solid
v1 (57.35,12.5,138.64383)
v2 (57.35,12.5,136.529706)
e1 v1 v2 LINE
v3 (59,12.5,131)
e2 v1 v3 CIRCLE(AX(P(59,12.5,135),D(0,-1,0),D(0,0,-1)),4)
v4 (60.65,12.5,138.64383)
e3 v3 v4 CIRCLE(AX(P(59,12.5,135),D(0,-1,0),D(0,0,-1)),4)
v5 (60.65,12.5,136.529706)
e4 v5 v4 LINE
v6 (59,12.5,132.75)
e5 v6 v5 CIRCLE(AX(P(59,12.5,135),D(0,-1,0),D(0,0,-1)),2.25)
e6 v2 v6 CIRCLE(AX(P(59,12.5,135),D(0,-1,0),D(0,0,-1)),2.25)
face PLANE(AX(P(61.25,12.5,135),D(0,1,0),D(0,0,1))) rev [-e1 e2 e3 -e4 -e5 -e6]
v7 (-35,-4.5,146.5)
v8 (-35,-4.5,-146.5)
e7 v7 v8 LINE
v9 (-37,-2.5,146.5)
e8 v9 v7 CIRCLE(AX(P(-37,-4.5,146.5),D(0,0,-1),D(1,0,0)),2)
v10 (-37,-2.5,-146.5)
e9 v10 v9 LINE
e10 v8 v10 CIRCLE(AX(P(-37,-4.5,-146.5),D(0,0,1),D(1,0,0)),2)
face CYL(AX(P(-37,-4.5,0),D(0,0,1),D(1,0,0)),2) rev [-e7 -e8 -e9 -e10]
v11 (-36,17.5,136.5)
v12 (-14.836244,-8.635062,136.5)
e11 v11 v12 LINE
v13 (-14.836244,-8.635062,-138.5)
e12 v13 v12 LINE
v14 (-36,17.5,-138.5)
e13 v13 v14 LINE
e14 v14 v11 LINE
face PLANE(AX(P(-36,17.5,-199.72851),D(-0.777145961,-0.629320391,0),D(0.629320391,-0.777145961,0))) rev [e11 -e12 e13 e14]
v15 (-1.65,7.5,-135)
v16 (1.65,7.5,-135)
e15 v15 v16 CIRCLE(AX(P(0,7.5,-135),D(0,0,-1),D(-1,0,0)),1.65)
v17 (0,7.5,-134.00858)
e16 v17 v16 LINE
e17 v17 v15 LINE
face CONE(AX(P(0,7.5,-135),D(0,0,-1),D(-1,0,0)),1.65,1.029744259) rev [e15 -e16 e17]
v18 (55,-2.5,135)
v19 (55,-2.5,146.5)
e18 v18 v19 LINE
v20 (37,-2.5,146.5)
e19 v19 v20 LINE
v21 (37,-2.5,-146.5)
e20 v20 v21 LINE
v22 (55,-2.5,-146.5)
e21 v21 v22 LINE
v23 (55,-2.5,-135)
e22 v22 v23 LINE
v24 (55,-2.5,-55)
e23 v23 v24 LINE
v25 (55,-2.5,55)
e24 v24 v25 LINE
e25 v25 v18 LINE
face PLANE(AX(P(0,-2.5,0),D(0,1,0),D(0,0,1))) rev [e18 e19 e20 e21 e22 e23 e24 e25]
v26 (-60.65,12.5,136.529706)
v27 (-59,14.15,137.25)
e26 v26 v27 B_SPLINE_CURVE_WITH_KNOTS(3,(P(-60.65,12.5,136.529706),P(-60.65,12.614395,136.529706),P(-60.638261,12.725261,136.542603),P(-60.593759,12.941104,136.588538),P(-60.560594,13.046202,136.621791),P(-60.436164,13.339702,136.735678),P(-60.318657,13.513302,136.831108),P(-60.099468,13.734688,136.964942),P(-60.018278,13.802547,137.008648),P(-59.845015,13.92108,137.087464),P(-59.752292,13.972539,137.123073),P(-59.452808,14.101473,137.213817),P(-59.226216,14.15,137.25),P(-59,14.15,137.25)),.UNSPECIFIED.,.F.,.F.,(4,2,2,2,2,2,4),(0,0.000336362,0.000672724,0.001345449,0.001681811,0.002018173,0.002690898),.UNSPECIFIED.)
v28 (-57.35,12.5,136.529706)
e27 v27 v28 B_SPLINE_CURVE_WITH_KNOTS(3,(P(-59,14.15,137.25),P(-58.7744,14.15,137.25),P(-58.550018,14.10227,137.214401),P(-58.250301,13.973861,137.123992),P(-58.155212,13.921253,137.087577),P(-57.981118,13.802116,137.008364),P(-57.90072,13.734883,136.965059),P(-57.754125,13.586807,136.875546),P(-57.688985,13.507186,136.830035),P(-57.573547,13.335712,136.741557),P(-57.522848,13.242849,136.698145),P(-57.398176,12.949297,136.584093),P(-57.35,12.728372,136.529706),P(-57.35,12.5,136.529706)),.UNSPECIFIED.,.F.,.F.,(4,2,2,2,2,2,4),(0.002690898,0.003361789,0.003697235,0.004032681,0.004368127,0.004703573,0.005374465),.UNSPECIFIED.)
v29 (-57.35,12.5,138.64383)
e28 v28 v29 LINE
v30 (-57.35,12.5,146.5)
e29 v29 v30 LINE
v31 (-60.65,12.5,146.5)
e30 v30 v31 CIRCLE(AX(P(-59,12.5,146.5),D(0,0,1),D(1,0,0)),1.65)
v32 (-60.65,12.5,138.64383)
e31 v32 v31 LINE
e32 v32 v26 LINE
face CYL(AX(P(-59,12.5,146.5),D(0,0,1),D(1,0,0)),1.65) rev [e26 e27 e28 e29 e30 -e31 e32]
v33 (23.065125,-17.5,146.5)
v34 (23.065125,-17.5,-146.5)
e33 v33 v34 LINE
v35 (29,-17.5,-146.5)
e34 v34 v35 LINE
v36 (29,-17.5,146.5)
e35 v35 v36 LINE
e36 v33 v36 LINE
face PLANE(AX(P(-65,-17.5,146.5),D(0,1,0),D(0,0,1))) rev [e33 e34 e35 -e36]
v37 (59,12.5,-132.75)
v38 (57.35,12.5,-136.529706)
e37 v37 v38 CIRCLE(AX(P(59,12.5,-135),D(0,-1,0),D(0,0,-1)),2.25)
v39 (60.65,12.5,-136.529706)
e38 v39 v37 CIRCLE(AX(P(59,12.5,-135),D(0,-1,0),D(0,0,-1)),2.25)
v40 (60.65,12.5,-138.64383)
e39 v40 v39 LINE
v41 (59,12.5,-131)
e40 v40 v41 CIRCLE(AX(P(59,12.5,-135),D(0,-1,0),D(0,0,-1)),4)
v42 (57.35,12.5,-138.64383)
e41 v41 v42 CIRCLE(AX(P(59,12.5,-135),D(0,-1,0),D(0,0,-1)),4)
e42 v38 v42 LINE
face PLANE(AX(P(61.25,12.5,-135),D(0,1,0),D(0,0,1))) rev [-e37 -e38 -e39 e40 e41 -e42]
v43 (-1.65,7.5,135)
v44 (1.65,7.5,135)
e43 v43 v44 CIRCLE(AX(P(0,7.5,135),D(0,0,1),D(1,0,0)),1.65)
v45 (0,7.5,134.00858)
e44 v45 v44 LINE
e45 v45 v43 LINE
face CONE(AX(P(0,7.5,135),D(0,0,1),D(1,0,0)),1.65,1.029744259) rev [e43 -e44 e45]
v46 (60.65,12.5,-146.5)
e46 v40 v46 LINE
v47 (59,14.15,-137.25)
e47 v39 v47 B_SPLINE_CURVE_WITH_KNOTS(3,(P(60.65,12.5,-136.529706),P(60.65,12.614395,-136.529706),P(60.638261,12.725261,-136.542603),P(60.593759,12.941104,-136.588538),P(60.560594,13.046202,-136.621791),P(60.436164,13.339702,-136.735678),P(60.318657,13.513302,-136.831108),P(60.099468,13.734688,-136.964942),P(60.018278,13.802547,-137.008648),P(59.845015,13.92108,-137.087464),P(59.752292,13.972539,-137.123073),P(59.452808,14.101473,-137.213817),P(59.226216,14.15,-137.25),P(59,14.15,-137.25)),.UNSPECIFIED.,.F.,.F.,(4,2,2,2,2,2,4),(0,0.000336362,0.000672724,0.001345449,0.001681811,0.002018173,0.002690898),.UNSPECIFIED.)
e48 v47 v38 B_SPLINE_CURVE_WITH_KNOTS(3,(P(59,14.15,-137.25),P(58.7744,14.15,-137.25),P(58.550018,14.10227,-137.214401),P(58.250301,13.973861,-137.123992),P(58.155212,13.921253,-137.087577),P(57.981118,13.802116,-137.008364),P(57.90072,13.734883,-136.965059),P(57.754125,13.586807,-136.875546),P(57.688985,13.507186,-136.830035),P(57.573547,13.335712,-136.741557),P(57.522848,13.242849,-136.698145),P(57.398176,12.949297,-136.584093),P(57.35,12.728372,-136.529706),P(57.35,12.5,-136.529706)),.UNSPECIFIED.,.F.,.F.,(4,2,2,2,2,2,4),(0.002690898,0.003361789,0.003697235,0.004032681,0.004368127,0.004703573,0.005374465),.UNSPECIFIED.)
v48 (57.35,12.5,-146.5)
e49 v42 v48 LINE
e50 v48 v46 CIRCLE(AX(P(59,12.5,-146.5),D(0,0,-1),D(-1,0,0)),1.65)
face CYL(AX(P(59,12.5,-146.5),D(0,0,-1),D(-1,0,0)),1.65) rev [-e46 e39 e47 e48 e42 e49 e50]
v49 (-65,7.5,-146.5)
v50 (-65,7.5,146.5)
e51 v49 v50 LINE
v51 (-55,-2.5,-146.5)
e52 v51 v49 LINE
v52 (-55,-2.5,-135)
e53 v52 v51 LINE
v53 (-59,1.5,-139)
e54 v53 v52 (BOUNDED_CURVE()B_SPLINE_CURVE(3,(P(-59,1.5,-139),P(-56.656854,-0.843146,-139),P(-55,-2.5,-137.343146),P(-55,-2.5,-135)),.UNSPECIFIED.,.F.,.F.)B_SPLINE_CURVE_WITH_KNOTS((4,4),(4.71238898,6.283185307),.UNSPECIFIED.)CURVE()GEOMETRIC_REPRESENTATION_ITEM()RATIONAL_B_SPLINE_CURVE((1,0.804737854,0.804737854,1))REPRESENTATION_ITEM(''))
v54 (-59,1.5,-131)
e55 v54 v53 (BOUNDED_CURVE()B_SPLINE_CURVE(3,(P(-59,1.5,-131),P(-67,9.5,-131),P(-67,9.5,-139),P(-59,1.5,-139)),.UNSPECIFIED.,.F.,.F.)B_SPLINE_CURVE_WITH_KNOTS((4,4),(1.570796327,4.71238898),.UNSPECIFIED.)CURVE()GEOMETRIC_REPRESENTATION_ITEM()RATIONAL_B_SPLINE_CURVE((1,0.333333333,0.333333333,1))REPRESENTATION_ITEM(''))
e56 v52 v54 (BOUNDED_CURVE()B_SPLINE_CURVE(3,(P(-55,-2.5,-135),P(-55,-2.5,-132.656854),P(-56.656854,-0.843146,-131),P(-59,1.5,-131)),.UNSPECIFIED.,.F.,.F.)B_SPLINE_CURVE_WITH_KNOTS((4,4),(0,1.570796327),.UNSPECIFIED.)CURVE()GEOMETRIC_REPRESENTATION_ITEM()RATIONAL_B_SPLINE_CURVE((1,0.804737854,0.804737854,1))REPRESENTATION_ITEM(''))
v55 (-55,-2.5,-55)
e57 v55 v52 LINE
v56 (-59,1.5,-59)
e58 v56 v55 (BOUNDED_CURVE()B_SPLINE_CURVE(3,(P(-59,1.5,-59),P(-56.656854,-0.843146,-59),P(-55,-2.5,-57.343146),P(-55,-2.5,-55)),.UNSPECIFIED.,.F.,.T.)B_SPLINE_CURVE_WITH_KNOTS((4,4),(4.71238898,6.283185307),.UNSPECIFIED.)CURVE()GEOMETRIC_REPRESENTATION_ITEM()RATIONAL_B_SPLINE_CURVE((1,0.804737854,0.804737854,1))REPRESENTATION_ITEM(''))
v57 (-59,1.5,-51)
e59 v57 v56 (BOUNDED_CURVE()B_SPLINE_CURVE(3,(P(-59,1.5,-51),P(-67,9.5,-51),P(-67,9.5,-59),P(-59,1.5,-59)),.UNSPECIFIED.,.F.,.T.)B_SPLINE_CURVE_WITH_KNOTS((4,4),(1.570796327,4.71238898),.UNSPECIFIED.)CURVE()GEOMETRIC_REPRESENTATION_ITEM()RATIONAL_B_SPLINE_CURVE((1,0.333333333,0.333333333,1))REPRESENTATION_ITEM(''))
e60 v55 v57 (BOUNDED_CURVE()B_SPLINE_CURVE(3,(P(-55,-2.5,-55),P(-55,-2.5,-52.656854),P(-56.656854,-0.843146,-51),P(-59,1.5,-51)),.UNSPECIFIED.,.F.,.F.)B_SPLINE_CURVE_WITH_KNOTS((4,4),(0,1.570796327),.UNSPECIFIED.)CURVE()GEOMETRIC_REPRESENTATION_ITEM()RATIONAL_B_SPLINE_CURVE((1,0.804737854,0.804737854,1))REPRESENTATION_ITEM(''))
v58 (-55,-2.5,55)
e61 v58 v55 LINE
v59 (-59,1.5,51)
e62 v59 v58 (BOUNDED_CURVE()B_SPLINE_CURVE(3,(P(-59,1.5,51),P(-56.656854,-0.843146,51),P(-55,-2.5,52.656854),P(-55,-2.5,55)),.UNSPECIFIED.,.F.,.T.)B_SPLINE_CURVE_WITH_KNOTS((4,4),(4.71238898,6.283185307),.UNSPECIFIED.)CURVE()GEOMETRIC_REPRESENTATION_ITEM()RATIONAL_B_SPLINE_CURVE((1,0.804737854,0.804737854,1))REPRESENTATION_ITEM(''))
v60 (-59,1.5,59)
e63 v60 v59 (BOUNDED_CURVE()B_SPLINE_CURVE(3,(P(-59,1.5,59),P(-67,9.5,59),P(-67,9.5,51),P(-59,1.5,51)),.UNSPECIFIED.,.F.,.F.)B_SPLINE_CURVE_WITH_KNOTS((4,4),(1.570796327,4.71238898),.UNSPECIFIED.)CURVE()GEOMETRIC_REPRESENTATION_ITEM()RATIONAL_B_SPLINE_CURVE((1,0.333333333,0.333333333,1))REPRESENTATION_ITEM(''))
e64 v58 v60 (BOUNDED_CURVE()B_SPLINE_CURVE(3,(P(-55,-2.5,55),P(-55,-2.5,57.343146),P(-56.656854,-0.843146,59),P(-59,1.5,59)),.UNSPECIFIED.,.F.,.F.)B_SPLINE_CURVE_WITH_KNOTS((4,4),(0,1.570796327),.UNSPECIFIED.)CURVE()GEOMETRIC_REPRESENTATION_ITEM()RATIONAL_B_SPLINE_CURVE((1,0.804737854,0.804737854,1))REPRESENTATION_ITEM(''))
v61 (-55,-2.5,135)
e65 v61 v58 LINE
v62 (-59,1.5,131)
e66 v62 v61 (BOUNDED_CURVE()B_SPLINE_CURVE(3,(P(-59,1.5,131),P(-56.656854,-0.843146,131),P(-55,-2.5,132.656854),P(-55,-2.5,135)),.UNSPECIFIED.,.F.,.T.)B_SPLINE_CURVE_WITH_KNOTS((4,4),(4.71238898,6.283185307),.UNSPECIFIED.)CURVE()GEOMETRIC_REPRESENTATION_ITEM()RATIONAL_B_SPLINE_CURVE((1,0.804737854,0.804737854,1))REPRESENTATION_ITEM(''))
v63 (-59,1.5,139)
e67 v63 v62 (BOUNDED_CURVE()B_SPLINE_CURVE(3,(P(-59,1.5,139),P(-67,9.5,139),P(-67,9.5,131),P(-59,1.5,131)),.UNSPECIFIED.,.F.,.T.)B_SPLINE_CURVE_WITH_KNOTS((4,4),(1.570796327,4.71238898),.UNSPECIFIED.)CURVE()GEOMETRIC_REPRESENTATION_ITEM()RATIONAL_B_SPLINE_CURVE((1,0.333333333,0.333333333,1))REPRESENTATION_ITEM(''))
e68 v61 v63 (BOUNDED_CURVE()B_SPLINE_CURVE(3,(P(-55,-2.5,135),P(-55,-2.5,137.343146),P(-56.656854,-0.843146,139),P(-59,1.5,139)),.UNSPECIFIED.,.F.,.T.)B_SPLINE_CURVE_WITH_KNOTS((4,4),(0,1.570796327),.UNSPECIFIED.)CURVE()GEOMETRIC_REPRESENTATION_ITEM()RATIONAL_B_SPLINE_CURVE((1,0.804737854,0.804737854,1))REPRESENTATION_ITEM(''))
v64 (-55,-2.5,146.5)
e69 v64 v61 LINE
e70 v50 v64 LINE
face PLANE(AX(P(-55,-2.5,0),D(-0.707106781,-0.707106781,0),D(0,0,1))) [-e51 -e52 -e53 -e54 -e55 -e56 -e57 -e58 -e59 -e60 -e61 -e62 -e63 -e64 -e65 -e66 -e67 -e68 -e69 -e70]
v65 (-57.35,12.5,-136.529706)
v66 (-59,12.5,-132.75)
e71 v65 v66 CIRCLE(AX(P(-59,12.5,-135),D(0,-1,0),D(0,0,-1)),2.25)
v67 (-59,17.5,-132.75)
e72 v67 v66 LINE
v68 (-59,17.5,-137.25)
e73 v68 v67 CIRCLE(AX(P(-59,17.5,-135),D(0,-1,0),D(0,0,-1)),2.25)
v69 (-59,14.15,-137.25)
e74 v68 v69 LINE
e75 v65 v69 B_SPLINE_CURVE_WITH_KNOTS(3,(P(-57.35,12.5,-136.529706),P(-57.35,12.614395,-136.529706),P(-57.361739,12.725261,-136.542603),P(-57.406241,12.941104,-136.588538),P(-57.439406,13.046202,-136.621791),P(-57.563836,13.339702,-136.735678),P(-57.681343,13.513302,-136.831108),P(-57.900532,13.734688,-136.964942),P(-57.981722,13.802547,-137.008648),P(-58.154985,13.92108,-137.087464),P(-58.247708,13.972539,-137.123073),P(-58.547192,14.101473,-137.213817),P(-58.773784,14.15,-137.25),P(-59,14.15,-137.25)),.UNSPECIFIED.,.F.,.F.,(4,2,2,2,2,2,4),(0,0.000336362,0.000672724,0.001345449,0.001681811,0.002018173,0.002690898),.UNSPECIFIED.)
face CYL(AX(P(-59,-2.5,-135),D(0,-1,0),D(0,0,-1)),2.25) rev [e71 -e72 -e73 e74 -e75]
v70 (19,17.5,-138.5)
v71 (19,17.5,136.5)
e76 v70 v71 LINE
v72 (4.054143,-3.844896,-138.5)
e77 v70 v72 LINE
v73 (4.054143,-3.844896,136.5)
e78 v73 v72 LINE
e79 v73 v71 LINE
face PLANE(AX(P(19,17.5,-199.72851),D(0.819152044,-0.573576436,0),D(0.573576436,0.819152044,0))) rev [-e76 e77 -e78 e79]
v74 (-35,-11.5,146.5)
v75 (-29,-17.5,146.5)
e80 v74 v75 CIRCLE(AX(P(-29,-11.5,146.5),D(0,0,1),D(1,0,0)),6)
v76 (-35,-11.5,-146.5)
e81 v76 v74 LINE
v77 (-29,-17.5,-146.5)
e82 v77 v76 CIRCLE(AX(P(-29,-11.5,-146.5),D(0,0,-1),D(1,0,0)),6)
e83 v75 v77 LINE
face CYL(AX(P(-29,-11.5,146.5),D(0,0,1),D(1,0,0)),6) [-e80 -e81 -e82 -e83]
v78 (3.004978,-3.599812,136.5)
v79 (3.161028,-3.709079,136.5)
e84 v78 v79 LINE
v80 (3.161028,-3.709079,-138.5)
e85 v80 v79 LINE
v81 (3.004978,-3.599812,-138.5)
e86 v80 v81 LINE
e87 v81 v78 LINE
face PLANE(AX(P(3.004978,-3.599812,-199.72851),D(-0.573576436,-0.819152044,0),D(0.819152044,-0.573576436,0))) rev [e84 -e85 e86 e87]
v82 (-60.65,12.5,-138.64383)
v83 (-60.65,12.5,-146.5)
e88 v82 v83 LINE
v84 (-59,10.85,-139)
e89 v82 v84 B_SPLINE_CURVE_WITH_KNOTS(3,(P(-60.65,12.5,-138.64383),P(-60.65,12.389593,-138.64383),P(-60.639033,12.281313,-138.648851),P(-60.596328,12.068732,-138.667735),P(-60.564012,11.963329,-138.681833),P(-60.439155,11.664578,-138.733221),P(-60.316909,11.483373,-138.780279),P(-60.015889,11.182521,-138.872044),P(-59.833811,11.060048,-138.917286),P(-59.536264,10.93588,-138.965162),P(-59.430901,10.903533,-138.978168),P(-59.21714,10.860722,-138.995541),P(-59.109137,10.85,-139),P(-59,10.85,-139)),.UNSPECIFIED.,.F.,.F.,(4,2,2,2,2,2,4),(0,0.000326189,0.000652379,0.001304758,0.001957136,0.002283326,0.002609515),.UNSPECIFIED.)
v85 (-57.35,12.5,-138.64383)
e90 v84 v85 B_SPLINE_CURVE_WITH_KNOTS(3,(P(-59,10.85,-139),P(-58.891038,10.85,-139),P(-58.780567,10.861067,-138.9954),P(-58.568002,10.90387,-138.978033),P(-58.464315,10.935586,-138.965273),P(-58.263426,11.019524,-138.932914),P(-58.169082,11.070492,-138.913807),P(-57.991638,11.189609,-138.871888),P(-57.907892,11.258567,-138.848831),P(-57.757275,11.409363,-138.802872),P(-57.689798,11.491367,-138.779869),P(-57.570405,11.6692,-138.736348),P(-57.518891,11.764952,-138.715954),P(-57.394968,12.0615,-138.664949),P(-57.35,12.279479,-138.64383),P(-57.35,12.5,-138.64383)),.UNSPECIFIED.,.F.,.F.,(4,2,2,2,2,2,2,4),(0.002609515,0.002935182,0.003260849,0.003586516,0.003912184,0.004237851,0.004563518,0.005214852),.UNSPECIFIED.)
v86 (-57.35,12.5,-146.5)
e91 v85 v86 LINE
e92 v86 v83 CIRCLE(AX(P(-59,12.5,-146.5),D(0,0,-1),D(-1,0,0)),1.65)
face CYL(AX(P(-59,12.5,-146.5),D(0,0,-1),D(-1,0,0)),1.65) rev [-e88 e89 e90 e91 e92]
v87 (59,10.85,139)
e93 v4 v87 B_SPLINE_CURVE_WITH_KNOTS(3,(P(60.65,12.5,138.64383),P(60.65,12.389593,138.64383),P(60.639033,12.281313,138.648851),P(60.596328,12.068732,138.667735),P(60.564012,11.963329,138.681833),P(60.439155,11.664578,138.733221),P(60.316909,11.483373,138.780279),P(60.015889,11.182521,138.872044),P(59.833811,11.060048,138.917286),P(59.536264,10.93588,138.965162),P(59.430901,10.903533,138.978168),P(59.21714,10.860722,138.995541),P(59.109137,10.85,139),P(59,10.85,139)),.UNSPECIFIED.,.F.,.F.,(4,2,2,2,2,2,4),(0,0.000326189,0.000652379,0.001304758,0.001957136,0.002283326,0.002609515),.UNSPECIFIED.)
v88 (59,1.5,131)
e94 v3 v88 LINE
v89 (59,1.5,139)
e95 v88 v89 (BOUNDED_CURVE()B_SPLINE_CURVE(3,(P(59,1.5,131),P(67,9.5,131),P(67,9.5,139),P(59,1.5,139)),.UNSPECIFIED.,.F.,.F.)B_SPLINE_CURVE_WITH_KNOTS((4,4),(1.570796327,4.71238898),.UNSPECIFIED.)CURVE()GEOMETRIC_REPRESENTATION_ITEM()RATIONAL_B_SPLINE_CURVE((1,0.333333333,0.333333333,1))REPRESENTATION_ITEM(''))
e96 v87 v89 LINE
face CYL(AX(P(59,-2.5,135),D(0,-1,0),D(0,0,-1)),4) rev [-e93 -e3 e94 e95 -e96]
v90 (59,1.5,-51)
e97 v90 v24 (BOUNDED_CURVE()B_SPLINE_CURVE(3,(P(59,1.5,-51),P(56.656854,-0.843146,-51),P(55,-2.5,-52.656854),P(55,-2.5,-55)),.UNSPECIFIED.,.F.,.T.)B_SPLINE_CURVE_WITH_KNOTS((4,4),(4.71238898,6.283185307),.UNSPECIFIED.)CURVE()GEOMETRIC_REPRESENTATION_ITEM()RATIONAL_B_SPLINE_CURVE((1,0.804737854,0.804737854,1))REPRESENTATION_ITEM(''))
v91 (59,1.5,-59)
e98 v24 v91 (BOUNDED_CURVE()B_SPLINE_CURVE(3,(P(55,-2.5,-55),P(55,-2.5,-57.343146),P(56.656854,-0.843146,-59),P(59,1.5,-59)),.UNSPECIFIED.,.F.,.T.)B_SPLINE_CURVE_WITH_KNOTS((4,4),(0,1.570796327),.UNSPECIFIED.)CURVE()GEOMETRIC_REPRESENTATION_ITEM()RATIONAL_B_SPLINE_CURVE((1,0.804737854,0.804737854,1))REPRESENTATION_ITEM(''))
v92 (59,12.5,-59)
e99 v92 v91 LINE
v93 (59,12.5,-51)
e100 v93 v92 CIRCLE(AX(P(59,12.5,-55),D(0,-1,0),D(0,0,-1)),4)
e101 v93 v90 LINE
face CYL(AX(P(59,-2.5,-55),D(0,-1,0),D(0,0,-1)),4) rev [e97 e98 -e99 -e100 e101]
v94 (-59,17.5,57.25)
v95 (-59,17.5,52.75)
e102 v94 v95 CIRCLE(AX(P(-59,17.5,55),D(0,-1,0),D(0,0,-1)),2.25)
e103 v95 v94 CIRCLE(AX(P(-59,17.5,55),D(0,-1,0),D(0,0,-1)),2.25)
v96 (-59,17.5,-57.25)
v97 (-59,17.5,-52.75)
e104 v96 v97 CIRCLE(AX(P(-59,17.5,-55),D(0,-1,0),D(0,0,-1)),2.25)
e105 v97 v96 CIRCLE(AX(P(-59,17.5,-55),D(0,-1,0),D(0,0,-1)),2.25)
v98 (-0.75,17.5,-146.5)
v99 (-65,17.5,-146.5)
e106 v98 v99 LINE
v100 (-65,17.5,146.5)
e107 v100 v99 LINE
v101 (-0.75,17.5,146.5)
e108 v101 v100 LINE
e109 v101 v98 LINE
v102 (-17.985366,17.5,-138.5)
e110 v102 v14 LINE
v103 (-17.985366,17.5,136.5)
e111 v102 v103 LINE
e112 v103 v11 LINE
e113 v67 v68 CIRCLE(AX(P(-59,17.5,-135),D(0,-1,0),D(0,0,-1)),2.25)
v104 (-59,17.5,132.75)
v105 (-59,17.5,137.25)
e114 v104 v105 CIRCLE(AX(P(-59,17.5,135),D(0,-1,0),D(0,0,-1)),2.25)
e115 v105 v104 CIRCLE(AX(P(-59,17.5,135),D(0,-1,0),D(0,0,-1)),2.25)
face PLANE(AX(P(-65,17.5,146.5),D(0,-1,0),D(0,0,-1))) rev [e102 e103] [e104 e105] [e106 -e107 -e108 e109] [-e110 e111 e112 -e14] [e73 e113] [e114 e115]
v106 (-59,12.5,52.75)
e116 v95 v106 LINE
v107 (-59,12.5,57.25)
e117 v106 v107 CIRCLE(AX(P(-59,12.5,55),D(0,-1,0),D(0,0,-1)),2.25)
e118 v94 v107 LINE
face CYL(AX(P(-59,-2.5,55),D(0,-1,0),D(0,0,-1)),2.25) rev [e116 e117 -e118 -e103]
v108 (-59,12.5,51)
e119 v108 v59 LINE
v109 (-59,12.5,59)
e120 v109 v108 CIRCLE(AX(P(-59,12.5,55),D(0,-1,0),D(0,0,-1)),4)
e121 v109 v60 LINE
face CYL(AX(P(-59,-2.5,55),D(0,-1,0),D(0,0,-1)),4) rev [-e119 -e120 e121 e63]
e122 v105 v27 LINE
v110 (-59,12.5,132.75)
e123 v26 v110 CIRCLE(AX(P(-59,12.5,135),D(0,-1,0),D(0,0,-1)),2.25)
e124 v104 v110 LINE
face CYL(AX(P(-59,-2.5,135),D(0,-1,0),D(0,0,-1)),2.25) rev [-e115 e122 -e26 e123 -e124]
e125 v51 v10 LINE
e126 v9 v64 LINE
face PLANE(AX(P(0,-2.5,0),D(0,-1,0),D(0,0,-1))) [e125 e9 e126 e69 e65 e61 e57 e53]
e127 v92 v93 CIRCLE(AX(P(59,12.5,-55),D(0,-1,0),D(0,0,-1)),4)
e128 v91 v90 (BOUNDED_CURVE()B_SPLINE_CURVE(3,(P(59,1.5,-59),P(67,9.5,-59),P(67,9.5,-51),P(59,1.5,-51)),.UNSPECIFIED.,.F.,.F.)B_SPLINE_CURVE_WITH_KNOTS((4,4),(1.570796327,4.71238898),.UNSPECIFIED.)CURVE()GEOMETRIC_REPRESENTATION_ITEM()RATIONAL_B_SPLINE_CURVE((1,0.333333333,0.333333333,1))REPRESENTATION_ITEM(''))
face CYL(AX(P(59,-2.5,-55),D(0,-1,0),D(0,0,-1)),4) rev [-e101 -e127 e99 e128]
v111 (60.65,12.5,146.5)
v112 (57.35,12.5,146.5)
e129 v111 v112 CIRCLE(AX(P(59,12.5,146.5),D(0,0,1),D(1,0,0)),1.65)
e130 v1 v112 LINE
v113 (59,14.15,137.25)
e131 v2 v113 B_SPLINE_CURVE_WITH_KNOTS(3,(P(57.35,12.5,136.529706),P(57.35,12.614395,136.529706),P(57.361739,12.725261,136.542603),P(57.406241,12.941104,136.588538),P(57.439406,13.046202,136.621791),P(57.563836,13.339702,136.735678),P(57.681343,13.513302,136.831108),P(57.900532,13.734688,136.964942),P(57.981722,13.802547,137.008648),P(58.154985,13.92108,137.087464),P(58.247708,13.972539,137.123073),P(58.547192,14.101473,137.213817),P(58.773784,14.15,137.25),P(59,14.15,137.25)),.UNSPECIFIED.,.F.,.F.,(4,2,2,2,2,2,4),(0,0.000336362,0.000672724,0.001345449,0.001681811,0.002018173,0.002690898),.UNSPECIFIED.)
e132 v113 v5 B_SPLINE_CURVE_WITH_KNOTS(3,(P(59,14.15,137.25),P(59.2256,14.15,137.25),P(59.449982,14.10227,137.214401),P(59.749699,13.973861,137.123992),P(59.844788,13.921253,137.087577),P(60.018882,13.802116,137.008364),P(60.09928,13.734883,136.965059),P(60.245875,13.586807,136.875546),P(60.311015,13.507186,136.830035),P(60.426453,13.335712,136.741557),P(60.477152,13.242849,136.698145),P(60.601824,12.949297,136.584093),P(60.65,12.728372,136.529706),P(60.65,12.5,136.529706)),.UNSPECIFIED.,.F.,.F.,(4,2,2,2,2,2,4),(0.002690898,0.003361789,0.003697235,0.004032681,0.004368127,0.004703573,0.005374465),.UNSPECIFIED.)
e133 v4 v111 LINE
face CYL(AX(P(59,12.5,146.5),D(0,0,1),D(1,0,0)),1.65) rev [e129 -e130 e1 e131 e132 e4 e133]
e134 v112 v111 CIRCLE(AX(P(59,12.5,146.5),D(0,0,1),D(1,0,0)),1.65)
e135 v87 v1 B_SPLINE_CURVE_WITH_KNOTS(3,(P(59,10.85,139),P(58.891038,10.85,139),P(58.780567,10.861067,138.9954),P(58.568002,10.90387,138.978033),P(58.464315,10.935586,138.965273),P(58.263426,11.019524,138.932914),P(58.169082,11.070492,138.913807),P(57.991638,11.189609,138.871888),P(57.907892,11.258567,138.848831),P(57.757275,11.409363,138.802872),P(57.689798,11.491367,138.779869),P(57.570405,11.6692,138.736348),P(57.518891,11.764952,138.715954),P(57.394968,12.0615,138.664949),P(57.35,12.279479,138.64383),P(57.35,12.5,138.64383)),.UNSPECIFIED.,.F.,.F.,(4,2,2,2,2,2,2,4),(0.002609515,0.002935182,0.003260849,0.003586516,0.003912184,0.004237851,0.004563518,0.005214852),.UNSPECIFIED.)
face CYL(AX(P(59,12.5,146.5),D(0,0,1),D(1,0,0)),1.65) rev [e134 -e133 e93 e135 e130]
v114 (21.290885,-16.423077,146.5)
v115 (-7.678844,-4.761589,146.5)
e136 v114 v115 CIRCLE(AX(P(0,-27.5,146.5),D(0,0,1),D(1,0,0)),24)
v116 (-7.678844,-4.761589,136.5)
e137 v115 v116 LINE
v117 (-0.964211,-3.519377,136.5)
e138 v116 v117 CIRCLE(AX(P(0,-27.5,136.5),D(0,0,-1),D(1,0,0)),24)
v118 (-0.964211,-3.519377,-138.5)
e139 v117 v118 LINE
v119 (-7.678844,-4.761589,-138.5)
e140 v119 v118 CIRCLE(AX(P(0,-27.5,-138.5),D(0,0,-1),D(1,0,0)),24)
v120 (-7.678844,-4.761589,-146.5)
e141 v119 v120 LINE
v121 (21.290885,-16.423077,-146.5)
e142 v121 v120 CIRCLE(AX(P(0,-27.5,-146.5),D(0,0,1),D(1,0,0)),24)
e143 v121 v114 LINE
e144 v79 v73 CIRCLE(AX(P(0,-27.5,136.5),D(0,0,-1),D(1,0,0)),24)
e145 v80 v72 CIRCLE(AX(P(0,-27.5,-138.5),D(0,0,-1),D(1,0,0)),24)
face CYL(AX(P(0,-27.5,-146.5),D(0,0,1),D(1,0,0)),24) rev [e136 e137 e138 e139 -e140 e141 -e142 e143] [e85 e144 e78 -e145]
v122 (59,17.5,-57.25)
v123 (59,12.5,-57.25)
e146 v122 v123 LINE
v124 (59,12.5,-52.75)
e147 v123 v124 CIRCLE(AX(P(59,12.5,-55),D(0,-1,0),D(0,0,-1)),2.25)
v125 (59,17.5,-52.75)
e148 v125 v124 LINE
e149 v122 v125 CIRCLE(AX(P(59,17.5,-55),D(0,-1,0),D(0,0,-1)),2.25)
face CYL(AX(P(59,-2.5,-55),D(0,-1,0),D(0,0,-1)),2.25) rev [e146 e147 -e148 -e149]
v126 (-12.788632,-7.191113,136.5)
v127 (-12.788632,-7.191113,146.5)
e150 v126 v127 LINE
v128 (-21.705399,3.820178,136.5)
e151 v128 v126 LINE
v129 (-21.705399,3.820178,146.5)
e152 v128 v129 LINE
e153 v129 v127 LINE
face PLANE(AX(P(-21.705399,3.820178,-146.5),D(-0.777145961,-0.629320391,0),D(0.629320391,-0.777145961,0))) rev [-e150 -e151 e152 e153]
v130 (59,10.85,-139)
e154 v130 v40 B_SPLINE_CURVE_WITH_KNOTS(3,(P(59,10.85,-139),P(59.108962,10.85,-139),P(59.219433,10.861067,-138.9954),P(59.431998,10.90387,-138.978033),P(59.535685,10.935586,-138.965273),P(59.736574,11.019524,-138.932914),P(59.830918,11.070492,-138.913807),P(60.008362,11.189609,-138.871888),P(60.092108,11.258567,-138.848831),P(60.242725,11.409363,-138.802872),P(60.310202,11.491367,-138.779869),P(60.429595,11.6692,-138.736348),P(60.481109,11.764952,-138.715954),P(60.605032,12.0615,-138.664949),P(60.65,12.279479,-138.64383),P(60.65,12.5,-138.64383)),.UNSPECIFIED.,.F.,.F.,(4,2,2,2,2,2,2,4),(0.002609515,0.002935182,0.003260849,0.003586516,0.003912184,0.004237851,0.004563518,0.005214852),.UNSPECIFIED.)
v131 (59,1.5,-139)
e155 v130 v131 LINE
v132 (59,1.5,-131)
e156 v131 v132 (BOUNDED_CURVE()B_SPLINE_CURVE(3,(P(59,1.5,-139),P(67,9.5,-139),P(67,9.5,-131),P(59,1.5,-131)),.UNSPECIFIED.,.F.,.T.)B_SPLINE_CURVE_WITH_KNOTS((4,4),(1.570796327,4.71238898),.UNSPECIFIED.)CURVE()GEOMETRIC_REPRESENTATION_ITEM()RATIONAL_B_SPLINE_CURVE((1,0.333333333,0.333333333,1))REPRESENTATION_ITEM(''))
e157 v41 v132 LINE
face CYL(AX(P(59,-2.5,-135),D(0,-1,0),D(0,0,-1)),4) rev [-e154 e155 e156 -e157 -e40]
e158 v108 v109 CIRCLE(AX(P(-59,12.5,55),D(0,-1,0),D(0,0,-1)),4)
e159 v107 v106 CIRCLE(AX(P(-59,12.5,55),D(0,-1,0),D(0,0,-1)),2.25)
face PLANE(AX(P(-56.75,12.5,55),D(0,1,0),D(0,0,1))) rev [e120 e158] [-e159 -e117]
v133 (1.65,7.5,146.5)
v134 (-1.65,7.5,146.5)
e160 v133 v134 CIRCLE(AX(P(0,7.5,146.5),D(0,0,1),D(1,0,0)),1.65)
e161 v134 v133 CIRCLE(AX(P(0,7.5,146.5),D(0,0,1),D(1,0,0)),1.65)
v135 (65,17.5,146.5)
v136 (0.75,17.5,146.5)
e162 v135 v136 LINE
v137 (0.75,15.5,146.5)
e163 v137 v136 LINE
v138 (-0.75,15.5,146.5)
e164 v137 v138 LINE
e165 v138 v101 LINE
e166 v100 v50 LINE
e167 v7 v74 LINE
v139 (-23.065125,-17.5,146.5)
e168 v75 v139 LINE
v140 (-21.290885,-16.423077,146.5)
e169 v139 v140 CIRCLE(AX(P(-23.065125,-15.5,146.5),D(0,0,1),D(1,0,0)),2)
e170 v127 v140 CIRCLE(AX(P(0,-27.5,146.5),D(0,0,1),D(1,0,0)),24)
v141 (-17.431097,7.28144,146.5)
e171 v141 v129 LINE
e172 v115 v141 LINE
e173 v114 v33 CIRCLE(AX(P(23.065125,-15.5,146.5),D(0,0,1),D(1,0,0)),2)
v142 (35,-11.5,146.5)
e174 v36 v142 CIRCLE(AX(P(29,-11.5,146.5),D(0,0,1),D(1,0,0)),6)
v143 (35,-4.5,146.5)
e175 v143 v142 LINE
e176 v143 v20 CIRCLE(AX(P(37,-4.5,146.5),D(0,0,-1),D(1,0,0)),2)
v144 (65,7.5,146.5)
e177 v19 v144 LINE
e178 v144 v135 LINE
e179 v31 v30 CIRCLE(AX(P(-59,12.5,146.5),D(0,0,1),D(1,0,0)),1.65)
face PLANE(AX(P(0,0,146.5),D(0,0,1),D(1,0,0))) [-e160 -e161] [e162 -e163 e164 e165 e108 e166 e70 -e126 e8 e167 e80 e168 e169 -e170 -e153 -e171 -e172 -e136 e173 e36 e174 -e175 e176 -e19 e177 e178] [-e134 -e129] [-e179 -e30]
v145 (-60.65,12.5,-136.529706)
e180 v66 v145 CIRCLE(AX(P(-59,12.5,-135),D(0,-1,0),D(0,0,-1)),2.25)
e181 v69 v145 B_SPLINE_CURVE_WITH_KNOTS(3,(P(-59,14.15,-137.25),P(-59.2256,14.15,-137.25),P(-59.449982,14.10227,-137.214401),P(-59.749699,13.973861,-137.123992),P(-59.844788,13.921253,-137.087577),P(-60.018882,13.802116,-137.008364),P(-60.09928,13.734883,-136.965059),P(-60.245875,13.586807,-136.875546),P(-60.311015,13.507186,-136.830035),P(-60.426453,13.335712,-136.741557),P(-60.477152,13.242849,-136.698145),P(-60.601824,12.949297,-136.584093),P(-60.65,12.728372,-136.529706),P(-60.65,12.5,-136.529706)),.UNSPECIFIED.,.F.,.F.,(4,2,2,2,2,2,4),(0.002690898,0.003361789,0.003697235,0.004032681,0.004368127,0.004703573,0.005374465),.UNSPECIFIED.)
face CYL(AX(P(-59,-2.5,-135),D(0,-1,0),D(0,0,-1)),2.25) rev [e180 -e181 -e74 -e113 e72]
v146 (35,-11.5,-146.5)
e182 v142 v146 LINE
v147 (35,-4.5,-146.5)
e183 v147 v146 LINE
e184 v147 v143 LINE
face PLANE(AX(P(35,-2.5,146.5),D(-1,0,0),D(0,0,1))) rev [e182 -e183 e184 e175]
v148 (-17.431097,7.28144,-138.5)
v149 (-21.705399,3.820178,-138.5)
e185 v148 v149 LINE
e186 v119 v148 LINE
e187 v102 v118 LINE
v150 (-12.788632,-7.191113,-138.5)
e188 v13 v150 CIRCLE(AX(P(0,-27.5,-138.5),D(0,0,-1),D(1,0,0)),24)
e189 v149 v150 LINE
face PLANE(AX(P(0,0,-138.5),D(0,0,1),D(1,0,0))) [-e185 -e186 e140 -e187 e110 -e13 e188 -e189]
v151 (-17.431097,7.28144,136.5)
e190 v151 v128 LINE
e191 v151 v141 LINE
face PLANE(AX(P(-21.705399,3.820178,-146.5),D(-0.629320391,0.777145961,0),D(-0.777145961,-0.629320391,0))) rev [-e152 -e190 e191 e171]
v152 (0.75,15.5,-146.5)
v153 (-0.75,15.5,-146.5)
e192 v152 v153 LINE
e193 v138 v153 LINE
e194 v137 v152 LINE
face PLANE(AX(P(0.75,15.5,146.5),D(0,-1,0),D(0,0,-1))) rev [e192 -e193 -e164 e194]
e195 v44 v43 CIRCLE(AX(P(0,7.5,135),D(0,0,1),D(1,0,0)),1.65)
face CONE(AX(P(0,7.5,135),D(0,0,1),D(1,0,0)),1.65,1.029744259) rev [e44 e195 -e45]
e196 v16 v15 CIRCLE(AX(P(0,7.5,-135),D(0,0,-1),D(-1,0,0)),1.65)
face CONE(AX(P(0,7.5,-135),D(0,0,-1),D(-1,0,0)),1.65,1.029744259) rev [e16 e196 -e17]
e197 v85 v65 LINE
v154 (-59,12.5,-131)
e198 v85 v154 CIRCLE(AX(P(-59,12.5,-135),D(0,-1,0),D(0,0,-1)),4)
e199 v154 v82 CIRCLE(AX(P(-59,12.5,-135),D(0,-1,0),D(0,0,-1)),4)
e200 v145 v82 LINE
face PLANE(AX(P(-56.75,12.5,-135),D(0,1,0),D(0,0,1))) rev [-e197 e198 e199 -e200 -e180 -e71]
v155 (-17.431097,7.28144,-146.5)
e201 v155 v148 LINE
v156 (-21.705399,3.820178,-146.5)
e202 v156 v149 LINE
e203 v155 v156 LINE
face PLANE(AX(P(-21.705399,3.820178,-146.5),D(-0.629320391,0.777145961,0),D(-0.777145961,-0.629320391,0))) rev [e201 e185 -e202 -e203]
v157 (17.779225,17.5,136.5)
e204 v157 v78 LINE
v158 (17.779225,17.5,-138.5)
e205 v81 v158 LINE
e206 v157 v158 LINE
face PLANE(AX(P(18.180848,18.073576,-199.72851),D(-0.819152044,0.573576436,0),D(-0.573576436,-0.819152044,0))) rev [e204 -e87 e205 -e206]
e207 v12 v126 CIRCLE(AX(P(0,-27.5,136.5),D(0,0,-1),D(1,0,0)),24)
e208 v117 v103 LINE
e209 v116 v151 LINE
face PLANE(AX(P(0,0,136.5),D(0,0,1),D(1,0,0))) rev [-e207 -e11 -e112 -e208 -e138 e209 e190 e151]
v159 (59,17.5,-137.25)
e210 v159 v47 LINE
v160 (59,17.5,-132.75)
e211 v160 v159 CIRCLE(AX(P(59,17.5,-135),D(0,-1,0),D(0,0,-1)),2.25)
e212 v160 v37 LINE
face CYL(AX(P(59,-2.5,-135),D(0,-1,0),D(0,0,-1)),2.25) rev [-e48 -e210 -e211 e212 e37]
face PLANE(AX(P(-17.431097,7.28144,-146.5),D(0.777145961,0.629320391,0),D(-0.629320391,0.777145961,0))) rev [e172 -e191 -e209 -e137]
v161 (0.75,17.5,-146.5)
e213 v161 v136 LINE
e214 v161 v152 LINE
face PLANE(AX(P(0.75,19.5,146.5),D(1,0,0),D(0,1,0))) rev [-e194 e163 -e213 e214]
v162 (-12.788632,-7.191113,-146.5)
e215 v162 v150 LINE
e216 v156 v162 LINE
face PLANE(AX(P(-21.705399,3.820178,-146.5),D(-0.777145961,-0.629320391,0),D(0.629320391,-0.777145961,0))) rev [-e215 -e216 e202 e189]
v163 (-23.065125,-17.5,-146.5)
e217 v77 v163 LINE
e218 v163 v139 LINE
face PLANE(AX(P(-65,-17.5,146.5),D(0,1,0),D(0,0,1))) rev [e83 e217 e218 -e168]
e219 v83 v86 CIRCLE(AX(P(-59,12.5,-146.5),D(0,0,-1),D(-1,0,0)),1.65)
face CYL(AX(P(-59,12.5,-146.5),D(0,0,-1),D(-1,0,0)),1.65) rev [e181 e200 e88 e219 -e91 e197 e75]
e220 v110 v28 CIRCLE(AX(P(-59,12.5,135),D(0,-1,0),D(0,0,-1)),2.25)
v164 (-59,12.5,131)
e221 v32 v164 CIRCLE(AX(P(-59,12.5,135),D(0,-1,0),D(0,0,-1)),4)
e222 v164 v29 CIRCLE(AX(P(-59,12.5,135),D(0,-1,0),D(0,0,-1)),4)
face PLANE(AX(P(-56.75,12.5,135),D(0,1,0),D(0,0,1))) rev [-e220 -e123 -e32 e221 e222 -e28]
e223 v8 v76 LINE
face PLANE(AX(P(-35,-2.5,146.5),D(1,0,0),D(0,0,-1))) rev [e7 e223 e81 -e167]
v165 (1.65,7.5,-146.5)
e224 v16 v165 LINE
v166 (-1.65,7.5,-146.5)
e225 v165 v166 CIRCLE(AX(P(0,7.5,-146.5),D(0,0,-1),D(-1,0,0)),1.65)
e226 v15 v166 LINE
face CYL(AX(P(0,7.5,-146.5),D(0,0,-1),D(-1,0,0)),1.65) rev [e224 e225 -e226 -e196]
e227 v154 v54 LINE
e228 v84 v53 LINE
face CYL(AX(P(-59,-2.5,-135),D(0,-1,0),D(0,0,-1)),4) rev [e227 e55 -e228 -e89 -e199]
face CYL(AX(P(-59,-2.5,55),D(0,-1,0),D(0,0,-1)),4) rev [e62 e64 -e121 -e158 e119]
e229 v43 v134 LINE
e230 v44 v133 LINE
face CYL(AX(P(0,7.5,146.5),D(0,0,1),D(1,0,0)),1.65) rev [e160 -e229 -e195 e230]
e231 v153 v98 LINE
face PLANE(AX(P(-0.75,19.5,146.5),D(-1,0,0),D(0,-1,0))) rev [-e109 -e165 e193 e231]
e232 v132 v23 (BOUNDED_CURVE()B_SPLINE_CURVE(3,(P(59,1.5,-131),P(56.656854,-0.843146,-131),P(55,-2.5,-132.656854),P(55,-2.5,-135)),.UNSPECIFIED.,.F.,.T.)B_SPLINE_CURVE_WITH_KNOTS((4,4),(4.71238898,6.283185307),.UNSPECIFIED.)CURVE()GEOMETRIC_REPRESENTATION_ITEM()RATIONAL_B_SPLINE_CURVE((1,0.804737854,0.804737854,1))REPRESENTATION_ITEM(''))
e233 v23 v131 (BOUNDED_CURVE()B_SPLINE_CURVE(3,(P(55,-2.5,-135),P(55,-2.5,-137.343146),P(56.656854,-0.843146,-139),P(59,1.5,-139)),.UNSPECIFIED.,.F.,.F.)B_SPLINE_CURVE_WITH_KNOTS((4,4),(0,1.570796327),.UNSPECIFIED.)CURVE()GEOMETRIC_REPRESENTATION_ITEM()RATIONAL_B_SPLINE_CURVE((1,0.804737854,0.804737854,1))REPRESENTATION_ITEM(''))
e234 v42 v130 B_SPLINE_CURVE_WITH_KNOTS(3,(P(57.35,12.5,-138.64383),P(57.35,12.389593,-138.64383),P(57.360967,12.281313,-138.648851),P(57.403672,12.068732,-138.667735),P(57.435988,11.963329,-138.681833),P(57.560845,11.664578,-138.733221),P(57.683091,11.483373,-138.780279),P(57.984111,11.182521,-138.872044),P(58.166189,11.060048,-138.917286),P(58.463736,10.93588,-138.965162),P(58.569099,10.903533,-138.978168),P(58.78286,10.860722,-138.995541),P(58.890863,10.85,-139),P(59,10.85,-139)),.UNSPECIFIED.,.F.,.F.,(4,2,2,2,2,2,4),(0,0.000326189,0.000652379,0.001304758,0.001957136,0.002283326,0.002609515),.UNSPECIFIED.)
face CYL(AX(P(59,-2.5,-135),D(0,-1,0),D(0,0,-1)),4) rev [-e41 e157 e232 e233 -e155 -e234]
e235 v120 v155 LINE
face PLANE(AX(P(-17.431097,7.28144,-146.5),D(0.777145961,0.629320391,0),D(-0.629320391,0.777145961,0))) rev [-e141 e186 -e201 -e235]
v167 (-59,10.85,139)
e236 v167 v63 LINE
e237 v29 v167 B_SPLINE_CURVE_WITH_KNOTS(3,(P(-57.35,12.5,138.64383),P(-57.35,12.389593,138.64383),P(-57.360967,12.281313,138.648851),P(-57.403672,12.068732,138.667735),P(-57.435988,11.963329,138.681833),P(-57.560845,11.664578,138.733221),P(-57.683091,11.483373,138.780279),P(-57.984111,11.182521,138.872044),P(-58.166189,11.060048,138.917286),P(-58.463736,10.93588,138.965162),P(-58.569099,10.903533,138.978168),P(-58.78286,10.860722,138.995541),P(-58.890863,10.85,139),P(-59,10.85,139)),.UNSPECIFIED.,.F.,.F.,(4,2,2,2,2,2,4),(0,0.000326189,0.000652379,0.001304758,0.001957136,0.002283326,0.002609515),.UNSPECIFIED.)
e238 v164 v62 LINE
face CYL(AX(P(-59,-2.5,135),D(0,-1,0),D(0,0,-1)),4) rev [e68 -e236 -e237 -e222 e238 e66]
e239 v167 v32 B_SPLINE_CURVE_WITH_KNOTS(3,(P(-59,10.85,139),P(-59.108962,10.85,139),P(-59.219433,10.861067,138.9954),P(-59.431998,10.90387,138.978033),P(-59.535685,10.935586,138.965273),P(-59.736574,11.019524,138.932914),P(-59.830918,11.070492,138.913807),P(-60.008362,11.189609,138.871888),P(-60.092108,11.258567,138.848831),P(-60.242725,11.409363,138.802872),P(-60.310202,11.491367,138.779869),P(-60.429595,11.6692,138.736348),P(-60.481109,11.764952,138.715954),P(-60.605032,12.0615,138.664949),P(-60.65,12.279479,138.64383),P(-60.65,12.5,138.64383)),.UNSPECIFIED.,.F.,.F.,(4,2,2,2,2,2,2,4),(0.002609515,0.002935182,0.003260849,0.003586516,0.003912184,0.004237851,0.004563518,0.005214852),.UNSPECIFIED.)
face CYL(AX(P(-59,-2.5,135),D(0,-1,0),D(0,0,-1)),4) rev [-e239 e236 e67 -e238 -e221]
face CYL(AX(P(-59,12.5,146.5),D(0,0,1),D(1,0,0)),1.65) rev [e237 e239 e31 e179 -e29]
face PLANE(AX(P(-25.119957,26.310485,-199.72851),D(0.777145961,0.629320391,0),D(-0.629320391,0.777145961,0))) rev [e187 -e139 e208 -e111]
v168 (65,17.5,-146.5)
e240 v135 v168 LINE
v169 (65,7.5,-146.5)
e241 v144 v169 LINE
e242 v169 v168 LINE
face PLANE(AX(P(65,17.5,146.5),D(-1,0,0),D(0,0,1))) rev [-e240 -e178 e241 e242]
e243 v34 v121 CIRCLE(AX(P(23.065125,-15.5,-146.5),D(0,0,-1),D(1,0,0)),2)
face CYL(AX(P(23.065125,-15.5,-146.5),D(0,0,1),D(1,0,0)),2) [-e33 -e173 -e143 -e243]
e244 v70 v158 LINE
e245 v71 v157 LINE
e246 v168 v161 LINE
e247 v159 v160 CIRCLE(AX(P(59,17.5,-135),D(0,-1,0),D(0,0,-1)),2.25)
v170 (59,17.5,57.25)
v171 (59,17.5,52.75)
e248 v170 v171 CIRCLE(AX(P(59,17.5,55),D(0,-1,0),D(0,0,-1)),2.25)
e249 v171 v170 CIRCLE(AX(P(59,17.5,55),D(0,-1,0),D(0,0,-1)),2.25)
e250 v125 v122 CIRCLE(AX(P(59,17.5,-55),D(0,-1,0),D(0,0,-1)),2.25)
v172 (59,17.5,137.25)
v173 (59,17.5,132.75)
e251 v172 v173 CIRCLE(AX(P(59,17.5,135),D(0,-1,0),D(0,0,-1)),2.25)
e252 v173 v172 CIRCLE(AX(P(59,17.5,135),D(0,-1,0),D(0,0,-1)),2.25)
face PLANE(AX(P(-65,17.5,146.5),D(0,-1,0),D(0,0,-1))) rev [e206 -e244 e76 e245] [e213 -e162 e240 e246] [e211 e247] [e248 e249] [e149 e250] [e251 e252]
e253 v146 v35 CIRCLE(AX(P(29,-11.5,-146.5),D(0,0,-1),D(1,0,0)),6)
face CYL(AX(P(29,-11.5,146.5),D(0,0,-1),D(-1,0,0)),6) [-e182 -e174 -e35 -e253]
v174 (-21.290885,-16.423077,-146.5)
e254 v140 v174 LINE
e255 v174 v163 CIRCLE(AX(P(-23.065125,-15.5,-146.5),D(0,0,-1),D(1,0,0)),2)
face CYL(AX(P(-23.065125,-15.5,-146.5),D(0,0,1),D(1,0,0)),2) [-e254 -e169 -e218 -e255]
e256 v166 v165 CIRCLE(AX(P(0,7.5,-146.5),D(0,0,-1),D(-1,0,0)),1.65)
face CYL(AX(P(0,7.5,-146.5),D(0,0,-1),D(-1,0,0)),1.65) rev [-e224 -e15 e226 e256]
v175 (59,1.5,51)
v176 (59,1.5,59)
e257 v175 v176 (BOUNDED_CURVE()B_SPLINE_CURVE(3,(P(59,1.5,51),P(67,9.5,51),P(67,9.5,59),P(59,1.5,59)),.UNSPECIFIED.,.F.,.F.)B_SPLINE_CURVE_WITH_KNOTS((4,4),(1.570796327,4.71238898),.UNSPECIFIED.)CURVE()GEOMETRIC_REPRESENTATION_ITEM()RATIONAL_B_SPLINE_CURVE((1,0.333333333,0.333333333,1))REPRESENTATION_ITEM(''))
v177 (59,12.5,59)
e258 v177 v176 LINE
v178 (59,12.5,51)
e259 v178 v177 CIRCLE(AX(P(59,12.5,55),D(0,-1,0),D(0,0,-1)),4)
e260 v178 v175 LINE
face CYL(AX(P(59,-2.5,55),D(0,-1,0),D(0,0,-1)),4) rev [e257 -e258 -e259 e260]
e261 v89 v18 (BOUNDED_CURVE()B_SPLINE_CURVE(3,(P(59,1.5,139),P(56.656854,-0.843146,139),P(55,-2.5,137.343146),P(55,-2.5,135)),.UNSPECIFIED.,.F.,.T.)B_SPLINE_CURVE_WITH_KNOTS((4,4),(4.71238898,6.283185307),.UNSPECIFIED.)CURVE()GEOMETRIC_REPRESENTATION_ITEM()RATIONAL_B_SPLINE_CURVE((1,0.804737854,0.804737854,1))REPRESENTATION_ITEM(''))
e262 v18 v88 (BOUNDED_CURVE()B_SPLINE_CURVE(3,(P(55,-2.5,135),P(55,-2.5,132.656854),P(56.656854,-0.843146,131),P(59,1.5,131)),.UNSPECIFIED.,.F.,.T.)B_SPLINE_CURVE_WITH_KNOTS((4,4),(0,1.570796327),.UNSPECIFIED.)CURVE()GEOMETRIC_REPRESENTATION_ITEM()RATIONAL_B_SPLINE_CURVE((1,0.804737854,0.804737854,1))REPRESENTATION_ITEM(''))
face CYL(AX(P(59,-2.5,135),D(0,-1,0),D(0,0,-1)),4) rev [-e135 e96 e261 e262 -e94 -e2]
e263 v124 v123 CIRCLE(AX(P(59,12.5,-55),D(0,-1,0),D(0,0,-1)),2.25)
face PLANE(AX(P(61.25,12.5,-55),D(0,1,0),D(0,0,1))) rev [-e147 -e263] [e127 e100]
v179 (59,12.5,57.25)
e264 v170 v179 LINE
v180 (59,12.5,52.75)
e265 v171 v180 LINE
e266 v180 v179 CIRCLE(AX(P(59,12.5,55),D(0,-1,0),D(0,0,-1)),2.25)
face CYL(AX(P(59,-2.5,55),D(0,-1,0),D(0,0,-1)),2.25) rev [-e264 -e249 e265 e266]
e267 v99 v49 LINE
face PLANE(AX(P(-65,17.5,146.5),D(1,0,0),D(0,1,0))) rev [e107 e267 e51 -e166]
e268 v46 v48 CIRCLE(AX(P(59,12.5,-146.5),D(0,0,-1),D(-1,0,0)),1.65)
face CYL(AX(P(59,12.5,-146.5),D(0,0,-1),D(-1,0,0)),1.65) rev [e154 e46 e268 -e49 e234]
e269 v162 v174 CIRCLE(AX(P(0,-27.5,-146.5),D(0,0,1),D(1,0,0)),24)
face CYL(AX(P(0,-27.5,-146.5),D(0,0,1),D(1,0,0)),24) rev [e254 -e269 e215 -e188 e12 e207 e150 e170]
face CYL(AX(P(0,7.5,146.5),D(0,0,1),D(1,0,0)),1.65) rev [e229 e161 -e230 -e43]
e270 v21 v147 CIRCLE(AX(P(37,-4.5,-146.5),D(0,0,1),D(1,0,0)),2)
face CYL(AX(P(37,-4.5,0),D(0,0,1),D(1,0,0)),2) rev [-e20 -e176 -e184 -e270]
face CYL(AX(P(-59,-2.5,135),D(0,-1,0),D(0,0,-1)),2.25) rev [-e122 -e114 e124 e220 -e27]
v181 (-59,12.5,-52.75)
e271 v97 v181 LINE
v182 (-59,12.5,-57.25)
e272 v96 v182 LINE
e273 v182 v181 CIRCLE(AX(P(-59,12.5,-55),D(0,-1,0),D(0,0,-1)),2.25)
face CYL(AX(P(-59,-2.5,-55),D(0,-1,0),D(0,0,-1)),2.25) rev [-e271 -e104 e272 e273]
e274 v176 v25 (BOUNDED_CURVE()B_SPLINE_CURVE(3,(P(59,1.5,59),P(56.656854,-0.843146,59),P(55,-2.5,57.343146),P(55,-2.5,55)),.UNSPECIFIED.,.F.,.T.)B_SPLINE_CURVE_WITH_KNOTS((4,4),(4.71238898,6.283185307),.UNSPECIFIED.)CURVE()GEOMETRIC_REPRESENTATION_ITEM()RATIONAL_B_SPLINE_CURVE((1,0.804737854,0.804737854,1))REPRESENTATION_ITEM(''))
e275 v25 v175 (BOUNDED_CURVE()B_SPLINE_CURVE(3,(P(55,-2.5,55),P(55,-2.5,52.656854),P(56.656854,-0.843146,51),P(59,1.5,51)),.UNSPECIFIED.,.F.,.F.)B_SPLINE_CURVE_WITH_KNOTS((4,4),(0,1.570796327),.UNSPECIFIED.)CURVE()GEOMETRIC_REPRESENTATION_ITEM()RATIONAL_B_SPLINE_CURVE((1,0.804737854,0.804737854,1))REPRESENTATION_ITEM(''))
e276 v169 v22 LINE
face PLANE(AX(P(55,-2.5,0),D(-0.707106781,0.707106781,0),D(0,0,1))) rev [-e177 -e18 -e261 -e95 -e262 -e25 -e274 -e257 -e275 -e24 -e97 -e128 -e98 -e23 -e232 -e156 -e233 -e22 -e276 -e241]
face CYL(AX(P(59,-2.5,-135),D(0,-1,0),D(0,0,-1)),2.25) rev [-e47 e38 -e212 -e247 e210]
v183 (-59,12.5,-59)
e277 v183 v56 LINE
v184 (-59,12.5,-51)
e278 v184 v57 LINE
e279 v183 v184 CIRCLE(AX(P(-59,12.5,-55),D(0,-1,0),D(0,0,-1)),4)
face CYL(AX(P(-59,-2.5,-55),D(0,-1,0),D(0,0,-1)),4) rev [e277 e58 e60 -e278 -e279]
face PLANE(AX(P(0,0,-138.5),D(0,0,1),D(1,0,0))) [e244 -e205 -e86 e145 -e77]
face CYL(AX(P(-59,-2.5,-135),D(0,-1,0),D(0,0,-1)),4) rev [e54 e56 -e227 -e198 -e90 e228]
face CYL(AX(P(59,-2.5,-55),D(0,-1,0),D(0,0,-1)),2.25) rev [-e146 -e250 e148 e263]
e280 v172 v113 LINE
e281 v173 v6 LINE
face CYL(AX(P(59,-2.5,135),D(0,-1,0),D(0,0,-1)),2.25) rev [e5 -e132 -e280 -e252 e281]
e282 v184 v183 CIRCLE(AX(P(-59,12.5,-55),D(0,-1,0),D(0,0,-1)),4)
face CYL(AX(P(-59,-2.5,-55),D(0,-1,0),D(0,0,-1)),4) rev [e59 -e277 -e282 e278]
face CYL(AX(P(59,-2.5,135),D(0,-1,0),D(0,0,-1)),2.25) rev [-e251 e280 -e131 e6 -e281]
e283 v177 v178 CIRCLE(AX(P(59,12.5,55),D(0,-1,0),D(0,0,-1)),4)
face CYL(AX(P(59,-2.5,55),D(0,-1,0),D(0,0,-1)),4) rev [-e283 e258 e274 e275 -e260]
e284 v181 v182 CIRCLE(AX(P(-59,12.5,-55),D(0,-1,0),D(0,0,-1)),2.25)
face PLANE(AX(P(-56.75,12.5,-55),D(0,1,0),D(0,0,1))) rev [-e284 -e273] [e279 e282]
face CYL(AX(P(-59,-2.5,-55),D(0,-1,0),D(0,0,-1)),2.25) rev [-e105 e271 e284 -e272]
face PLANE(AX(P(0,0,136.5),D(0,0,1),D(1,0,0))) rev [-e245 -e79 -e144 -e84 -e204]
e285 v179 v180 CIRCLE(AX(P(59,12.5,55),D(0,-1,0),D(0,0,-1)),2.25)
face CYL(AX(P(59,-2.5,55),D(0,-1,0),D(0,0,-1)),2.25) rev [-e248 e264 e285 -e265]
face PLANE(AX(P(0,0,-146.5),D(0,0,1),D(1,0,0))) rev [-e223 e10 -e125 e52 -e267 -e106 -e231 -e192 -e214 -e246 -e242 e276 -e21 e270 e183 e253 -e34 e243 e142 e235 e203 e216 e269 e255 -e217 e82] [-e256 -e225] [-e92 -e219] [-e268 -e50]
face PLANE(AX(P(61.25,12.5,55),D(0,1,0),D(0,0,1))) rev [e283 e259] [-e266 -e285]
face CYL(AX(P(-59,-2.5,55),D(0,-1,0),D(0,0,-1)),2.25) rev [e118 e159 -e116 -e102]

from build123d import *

# Parameters (mm, degrees)
SKETCH1_W                                            = 130
SKETCH1_H                                            = 35
BOSS_EXTRUDE1_DEPTH                                  = 146.5
SKETCH3_R                                            = 24
CUT_EXTRUDE2_DEPTH                                   = 301.633082012
SKETCH7_W                                            = 30
SKETCH7_H                                            = 293
CUT_EXTRUDE5_DEPTH                                   = 15
FILLET1_R                                            = 6
CHAMFER1_SIZE                                        = 10
FILLET2_R                                            = 2
CUT_EXTRUDE6_DEPTH                                   = 275
CUT_EXTRUDE8_DEPTH                                   = 301.633082012
FILLET3_R                                            = 2
M4_TAPPED_HOLE1_AT_2_COUNT                           = 2
M4_TAPPED_HOLE1_AT_2_PITCH                           = 59.211485372
M4_TAPPED_HOLE1_AT_3_COUNT                           = 2
M4_TAPPED_HOLE1_AT_3_PITCH                           = 59.211485372
SKETCH15_W                                           = 1.5
SKETCH15_H                                           = 4
CUT_EXTRUDE9_DEPTH                                   = 301.633082012
HOLE_SIZE_PER_SOCKET_HEAD_CAP_SCREW_TYPE_D           = 4.5
HOLE_SIZE_PER_SOCKET_HEAD_CAP_SCREW_TYPE_CBORE_D     = 8
HOLE_SIZE_PER_SOCKET_HEAD_CAP_SCREW_TYPE_CBORE_DEPTH = 15
LPATTERN1_COUNT                                      = 2
LPATTERN1_PITCH                                      = 80
MIRROR2_COPY_1_D                                     = 4.5
MIRROR2_COPY_1_CBORE_D                               = 8
MIRROR2_COPY_1_CBORE_DEPTH                           = 15


with BuildPart() as part:
    # Sketch1 → Boss-Extrude1 (new, symmetric)
    with BuildSketch(Plane.XY):
        Rectangle(SKETCH1_W, SKETCH1_H)
    extrude(amount=BOSS_EXTRUDE1_DEPTH, both=True)

    # Sketch3 → Cut-Extrude2 (cut, through all)
    with BuildSketch(Plane.XY.offset(146.5)):
        with Locations((0, -27.5)):
            Circle(SKETCH3_R)
    extrude(amount=-CUT_EXTRUDE2_DEPTH, mode=Mode.SUBTRACT)

    # Sketch7 → Cut-Extrude5 (cut)
    with BuildSketch(Plane.XZ.offset(17.5)):
        with Locations((-50, 0)):
            Rectangle(SKETCH7_W, SKETCH7_H)
        with Locations((50, 0)):
            Rectangle(SKETCH7_W, SKETCH7_H)
    extrude(amount=-CUT_EXTRUDE5_DEPTH, mode=Mode.SUBTRACT)

    # Fillet1
    fillet1_edges = [part.edges().sort_by_distance(p)[0] for p in [
        (-35, -17.5, 0),
        (35, -17.5, 0),
    ]]
    fillet(fillet1_edges, radius=FILLET1_R)

    # Chamfer1
    chamfer1_edges = [part.edges().sort_by_distance(p)[0] for p in [
        (-65, -2.5, 0),
        (65, -2.5, 0),
    ]]
    chamfer(chamfer1_edges, length=CHAMFER1_SIZE)

    # Fillet2
    fillet2_edges = [part.edges().sort_by_distance(p)[0] for p in [
        (-35, -2.5, 0),
        (35, -2.5, 0),
    ]]
    fillet(fillet2_edges, radius=FILLET2_R)

    # Sketch8 → Cut-Extrude6 (cut)
    with BuildSketch(Plane.XY.offset(136.5)):
        Polygon((-36, 17.5), (-25.11995654, 26.310485475), (-0.29024799, -4.351651011), (-11.170291451, -13.162136485), align=None)
        Polygon((18.180847956, 18.073576436), (19, 17.5), (3.82412996, -4.173388548), (3.004977916, -3.599812112), align=None)
    extrude(amount=-CUT_EXTRUDE6_DEPTH, mode=Mode.SUBTRACT)

    # Sketch10 → Cut-Extrude8 (cut, through all)
    with BuildSketch(Plane.XY.offset(146.5)):
        Polygon((-21.705399374, 3.820177656), (-17.431096586, 7.281439807), (-4.844688765, -8.261479422), (-9.118991553, -11.722741573), align=None)
    extrude(amount=-CUT_EXTRUDE8_DEPTH, mode=Mode.SUBTRACT)

    # Fillet3
    fillet3_edges = [part.edges().sort_by_distance(p)[0] for p in [
        (-21.817424229, -17.5, 0),
        (21.817424229, -17.5, 0),
    ]]
    fillet(fillet3_edges, radius=FILLET3_R)

    # Sketch11 → M4 Tapped Hole1 (revolve, cut)
    with BuildSketch(Plane(origin=(0, 7.5, 146.5), x_dir=(0, -1, 0), z_dir=(1, 0, 0))):
        Polygon((0, 0), (0, 12.491420021), (1.65, 11.5), (1.65, 0), align=None)
    m4_tapped_hole1 = revolve(axis=Axis((0, 7.5, 152.85), (0, 0, -1)), mode=Mode.SUBTRACT)

    # M4 Tapped Hole1 at 2: M4 Tapped Hole1 ×2
    with Locations(*[Vector(0.9964283048969313, 0.08444307668618053, 0) * (i * M4_TAPPED_HOLE1_AT_2_PITCH) for i in range(1, M4_TAPPED_HOLE1_AT_2_COUNT)]):
        add(m4_tapped_hole1, mode=Mode.SUBTRACT)

    # M4 Tapped Hole1 at 3: M4 Tapped Hole1 ×2
    with Locations(*[Vector(-0.9964283048969313, 0.08444307668618053, 0) * (i * M4_TAPPED_HOLE1_AT_3_PITCH) for i in range(1, M4_TAPPED_HOLE1_AT_3_COUNT)]):
        add(m4_tapped_hole1, mode=Mode.SUBTRACT)

    # Mirror1: M4 Tapped Hole1 across plane
    add(m4_tapped_hole1.mirror(Plane.XY), mode=Mode.SUBTRACT)

    # Mirror1 copy 1 sketch → Mirror1 copy 1 (revolve, cut)
    with BuildSketch(Plane(origin=(59, 12.5, -146.5), x_dir=(0, -1, 0), z_dir=(1, 0, 0))):
        Polygon((0, 0), (0, -12.491420021), (1.65, -11.5), (1.65, 0), align=None)
    revolve(axis=Axis((59, 12.5, -152.85), (0, 0, -1)), mode=Mode.SUBTRACT)

    # Mirror1 copy 2 sketch → Mirror1 copy 2 (revolve, cut)
    with BuildSketch(Plane(origin=(-59, 12.5, -146.5), x_dir=(0, -1, 0), z_dir=(1, 0, 0))):
        Polygon((0, 0), (0, -12.491420021), (1.65, -11.5), (1.65, 0), align=None)
    revolve(axis=Axis((-59, 12.5, -152.85), (0, 0, -1)), mode=Mode.SUBTRACT)

    # Sketch15 → Cut-Extrude9 (cut, through all)
    with BuildSketch(Plane(origin=(0, 0, -146.5), x_dir=(-1, 0, 0), z_dir=(0, 0, -1))):
        with Locations((0, 17.5)):
            Rectangle(SKETCH15_W, SKETCH15_H)
    extrude(amount=-CUT_EXTRUDE9_DEPTH, mode=Mode.SUBTRACT)

    # Hole size per socket head cap screw type 1 (through all)
    with Locations(Plane(origin=(0, -2.5, 0), x_dir=(-1, 0, 0), z_dir=(0, -1, 0))):
        with Locations((59, -135), (-59, -135)):
            hole_size_per_socket_head_cap_screw_type = CounterBoreHole(HOLE_SIZE_PER_SOCKET_HEAD_CAP_SCREW_TYPE_D / 2, HOLE_SIZE_PER_SOCKET_HEAD_CAP_SCREW_TYPE_CBORE_D / 2, HOLE_SIZE_PER_SOCKET_HEAD_CAP_SCREW_TYPE_CBORE_DEPTH)

    # LPattern1: Hole size per socket head cap screw type 1 ×2
    with Locations(*[(0, 0, -i * LPATTERN1_PITCH) for i in range(1, LPATTERN1_COUNT)]):
        add(hole_size_per_socket_head_cap_screw_type, mode=Mode.SUBTRACT)

    # Mirror2: Hole size per socket head cap screw type 1 across plane
    add(hole_size_per_socket_head_cap_screw_type.mirror(Plane.XY), mode=Mode.SUBTRACT)

    # Mirror2 copy 1 (through all)
    with Locations(Plane(origin=(0, -2.5, 80), x_dir=(-1, 0, 0), z_dir=(0, -1, 0))):
        with Locations((59, 135), (-59, 135)):
            CounterBoreHole(MIRROR2_COPY_1_D / 2, MIRROR2_COPY_1_CBORE_D / 2, MIRROR2_COPY_1_CBORE_DEPTH)


solid = part.part
